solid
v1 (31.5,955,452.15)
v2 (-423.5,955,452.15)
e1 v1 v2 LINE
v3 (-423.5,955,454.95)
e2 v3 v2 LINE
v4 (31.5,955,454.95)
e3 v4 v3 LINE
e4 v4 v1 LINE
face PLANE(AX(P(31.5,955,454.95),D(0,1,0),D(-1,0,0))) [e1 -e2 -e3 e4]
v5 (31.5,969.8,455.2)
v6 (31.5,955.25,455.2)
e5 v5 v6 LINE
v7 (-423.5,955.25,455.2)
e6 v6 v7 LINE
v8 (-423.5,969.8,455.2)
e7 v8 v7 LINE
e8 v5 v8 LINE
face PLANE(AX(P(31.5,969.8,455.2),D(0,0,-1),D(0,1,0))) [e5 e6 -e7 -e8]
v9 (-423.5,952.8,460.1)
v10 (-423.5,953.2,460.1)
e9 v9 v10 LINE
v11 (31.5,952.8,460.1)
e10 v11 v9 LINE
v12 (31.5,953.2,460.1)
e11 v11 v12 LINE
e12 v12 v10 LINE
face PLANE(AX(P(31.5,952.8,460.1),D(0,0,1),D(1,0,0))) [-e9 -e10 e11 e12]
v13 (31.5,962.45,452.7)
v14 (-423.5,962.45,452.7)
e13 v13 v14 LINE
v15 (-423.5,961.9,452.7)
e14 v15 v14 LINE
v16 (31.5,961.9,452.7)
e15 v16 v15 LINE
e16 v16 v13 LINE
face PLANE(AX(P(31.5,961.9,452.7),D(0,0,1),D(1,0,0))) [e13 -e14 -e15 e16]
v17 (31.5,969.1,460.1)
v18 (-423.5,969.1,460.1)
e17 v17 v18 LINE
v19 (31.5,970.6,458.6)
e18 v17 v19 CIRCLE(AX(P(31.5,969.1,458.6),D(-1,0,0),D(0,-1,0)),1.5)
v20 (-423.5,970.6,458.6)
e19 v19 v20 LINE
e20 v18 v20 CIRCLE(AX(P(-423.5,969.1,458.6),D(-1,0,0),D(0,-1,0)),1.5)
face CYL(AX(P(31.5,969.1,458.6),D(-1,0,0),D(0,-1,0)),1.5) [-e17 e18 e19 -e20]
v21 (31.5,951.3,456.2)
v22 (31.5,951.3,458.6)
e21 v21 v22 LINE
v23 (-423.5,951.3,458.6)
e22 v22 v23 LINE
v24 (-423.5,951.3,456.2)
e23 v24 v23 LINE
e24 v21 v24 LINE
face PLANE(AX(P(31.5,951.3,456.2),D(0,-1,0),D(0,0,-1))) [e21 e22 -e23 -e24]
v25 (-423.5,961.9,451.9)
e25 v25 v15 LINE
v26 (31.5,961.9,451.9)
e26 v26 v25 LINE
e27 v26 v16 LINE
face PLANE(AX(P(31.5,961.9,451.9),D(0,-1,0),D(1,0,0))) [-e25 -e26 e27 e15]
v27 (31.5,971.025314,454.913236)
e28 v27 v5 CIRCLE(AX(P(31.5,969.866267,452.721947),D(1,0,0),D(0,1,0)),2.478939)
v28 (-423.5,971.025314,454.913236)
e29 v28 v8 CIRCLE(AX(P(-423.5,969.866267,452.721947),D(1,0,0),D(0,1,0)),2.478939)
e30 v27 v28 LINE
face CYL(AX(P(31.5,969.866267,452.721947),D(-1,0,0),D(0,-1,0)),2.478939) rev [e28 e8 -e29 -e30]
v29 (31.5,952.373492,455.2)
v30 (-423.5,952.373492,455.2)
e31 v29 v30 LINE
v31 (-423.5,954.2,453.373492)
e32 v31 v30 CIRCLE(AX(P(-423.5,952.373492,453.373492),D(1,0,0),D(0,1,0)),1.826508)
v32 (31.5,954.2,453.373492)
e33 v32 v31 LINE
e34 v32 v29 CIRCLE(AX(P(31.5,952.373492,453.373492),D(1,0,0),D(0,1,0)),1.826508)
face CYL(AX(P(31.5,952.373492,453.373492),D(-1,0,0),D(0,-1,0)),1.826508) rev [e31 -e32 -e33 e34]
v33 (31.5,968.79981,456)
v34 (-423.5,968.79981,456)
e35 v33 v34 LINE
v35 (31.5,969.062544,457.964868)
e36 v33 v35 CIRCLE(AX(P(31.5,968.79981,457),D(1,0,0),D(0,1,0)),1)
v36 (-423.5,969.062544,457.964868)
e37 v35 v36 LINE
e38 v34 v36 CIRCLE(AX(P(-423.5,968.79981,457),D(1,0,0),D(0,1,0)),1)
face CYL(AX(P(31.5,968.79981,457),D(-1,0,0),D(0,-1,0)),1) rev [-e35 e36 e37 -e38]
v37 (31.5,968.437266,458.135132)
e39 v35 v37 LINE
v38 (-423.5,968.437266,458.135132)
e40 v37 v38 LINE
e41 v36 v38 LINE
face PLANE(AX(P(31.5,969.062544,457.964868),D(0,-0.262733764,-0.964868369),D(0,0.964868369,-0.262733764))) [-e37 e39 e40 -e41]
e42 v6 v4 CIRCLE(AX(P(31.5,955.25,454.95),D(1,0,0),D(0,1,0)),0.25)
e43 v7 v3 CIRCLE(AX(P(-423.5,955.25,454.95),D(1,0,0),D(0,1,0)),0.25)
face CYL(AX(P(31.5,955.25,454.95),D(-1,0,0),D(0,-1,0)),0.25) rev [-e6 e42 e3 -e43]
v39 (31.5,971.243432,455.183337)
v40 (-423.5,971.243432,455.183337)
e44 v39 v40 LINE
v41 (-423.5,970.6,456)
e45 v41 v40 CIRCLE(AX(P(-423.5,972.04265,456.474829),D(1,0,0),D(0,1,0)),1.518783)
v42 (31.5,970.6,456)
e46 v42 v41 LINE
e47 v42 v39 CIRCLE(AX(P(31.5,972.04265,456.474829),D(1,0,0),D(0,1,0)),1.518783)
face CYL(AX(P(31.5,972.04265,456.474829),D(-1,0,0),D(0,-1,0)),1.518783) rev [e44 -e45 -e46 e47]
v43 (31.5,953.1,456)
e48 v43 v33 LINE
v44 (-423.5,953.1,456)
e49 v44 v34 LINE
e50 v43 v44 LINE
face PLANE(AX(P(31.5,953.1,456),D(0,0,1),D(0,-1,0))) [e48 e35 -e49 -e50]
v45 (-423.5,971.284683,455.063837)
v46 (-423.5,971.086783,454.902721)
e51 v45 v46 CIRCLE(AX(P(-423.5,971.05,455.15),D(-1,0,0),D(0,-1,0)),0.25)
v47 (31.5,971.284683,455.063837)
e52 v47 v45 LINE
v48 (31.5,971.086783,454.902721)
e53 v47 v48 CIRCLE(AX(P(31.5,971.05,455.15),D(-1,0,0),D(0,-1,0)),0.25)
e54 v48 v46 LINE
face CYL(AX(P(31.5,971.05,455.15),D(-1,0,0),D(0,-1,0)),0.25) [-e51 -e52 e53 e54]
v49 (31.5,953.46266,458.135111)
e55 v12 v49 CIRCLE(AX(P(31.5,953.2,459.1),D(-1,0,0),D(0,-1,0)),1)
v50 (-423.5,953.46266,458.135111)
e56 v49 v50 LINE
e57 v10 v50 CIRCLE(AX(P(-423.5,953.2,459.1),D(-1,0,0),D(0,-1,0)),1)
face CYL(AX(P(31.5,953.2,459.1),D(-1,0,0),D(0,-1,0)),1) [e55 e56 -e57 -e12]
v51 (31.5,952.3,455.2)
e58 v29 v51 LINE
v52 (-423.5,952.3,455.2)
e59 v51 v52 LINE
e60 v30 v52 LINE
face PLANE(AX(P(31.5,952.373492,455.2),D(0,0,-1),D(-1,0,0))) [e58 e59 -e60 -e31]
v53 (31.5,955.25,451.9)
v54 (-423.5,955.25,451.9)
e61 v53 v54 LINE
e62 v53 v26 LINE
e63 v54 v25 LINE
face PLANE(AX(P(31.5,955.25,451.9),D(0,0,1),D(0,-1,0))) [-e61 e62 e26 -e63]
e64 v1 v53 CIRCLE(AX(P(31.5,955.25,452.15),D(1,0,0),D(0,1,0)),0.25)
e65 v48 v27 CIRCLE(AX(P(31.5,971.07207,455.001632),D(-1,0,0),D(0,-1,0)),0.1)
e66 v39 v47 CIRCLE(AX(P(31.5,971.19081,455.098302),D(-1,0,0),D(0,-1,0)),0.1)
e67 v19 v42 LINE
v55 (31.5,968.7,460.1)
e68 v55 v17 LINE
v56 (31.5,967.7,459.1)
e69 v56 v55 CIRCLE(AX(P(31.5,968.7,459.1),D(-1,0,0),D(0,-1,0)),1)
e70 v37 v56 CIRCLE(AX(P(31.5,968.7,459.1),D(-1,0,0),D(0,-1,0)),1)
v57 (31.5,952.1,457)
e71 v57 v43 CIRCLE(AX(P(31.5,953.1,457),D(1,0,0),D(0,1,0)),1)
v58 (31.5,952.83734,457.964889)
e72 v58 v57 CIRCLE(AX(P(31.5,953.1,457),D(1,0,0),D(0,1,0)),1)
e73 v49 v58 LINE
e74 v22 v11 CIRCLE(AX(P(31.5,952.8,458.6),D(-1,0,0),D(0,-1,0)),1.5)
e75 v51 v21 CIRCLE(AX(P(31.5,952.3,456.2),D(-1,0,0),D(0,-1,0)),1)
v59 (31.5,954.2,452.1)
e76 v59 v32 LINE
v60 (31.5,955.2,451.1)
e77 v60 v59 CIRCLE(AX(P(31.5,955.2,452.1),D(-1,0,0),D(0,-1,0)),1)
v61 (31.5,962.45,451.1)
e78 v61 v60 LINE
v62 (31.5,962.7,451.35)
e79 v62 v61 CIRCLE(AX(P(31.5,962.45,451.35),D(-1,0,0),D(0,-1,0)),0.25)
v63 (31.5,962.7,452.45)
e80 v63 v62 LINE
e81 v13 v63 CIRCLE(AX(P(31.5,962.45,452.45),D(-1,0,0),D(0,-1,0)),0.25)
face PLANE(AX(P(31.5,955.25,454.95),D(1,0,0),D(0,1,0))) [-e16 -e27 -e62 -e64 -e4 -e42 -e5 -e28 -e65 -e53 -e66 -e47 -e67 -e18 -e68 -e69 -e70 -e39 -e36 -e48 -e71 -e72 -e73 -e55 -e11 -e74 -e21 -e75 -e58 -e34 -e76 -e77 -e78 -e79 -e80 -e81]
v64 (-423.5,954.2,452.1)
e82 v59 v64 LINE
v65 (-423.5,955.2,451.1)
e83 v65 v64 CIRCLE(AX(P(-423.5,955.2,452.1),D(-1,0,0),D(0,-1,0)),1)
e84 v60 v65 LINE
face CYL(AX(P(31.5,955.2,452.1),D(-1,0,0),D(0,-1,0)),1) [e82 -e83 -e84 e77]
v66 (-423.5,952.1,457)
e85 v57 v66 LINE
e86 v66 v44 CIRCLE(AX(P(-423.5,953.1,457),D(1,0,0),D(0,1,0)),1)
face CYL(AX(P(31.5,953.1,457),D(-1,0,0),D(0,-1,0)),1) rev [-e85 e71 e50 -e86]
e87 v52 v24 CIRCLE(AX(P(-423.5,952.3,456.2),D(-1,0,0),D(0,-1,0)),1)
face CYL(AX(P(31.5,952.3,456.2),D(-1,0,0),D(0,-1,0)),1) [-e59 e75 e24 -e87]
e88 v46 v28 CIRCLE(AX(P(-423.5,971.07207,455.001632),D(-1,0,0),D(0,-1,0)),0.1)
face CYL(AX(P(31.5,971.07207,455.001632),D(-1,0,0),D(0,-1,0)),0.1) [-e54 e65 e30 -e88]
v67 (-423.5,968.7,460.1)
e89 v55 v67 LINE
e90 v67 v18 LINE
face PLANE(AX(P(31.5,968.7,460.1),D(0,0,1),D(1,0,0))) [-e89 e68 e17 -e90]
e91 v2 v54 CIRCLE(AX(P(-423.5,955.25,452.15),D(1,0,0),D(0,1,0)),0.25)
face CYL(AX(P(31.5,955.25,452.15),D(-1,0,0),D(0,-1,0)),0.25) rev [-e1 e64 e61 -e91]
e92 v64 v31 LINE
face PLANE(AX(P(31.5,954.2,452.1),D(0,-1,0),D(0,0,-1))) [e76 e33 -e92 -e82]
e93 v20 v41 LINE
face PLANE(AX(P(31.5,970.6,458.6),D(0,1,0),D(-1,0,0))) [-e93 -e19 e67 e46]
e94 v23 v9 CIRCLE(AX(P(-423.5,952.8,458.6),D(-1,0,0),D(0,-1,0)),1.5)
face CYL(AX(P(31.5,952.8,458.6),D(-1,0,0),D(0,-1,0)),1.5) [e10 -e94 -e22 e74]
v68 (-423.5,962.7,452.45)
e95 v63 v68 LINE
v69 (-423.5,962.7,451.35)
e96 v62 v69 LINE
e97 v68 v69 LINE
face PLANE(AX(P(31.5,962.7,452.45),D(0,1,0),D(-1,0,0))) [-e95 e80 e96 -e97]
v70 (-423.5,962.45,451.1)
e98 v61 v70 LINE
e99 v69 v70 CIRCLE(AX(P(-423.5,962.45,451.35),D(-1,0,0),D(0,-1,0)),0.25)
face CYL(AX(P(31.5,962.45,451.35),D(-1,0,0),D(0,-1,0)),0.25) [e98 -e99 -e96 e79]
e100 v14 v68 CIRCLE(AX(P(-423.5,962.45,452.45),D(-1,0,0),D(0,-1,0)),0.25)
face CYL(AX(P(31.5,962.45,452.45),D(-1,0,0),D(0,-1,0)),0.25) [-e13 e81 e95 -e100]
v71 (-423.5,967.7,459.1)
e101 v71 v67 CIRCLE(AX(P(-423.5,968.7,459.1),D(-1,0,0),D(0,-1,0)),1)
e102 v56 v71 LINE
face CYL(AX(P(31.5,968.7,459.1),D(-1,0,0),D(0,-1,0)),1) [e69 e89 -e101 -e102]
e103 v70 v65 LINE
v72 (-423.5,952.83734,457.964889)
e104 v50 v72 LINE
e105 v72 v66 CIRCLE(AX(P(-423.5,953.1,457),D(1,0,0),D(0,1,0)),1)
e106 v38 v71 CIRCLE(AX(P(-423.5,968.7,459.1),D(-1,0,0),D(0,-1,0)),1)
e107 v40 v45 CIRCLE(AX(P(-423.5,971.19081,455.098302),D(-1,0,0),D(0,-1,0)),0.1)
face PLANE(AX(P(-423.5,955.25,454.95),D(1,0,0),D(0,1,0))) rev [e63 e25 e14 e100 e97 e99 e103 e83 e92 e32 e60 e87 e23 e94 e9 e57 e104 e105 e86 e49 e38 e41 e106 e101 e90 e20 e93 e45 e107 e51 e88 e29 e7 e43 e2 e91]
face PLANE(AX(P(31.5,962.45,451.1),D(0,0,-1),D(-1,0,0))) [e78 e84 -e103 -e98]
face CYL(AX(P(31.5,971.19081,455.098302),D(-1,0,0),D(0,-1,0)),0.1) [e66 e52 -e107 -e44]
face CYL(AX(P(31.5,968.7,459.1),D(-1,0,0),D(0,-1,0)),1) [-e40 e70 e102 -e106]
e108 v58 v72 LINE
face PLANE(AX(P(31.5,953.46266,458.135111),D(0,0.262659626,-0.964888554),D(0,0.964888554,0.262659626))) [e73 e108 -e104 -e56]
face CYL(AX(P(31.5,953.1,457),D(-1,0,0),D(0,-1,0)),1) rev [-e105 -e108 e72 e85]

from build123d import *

# Parameters (mm, degrees)
BOSS_EXTRUDE1_DEPTH = 455


with BuildPart() as part:
    # Sketch1 → Boss-Extrude1 (new body)
    with BuildSketch(Plane(origin=(-423.5, 0, 0), x_dir=(0, -1, 0), z_dir=(-1, 0, 0))):
        with BuildLine():
            Line((-955, 454.95), (-955, 452.15))
            ThreePointArc((-955, 452.15), (-955.073223305, 451.973223305), (-955.25, 451.9))
            Line((-955.25, 451.9), (-961.9, 451.9))
            Line((-961.9, 451.9), (-961.9, 452.7))
            Line((-961.9, 452.7), (-962.45, 452.7))
            ThreePointArc((-962.45, 452.7), (-962.626776695, 452.626776695), (-962.7, 452.45))
            Line((-962.7, 452.45), (-962.7, 451.35))
            ThreePointArc((-962.7, 451.35), (-962.626776695, 451.173223305), (-962.45, 451.1))
            Line((-962.45, 451.1), (-955.2, 451.1))
            ThreePointArc((-955.2, 451.1), (-954.492893219, 451.392893219), (-954.2, 452.1))
            Line((-954.2, 452.1), (-954.2, 453.373491886))
            ThreePointArc((-954.2, 453.373491886), (-953.665028159, 454.665028159), (-952.373491886, 455.2))
            Line((-952.373491886, 455.2), (-952.3, 455.2))
            ThreePointArc((-952.3, 455.2), (-951.592893219, 455.492893219), (-951.3, 456.2))
            Line((-951.3, 456.2), (-951.3, 458.6))
            ThreePointArc((-951.3, 458.6), (-951.739339828, 459.660660172), (-952.8, 460.1))
            Line((-952.8, 460.1), (-953.2, 460.1))
            ThreePointArc((-953.2, 460.1), (-954.191183271, 459.232498012), (-953.462659626, 458.135111446))
            Line((-953.462659626, 458.135111446), (-952.837340374, 457.964888554))
            ThreePointArc((-952.837340374, 457.964888554), (-952.108816729, 456.867501988), (-953.1, 456))
            Line((-953.1, 456), (-968.799810447, 456))
            ThreePointArc((-968.799810447, 456), (-969.790988627, 456.867463908), (-969.062544211, 457.964868369))
            Line((-969.062544211, 457.964868369), (-968.437266236, 458.135131631))
            ThreePointArc((-968.437266236, 458.135131631), (-967.70882182, 459.232536092), (-968.7, 460.1))
            Line((-968.7, 460.1), (-969.1, 460.1))
            ThreePointArc((-969.1, 460.1), (-970.160660172, 459.660660172), (-970.6, 458.6))
            Line((-970.6, 458.6), (-970.6, 456))
            ThreePointArc((-970.6, 456), (-970.849658895, 455.534896264), (-971.243431907, 455.183337075))
            ThreePointArc((-971.243431907, 455.183337075), (-971.28533621, 455.130932577), (-971.284682745, 455.06383731))
            ThreePointArc((-971.284682745, 455.06383731), (-971.207838721, 454.956126495), (-971.086783129, 454.902720811))
            ThreePointArc((-971.086783129, 454.902720811), (-971.055207963, 454.903064362), (-971.025314114, 454.913236231))
            ThreePointArc((-971.025314114, 454.913236231), (-970.431156786, 455.135665686), (-969.8, 455.2))
            Line((-969.8, 455.2), (-955.25, 455.2))
            ThreePointArc((-955.25, 455.2), (-955.073223305, 455.126776695), (-955, 454.95))
        make_face()
    extrude(amount=-BOSS_EXTRUDE1_DEPTH)


solid = part.part
